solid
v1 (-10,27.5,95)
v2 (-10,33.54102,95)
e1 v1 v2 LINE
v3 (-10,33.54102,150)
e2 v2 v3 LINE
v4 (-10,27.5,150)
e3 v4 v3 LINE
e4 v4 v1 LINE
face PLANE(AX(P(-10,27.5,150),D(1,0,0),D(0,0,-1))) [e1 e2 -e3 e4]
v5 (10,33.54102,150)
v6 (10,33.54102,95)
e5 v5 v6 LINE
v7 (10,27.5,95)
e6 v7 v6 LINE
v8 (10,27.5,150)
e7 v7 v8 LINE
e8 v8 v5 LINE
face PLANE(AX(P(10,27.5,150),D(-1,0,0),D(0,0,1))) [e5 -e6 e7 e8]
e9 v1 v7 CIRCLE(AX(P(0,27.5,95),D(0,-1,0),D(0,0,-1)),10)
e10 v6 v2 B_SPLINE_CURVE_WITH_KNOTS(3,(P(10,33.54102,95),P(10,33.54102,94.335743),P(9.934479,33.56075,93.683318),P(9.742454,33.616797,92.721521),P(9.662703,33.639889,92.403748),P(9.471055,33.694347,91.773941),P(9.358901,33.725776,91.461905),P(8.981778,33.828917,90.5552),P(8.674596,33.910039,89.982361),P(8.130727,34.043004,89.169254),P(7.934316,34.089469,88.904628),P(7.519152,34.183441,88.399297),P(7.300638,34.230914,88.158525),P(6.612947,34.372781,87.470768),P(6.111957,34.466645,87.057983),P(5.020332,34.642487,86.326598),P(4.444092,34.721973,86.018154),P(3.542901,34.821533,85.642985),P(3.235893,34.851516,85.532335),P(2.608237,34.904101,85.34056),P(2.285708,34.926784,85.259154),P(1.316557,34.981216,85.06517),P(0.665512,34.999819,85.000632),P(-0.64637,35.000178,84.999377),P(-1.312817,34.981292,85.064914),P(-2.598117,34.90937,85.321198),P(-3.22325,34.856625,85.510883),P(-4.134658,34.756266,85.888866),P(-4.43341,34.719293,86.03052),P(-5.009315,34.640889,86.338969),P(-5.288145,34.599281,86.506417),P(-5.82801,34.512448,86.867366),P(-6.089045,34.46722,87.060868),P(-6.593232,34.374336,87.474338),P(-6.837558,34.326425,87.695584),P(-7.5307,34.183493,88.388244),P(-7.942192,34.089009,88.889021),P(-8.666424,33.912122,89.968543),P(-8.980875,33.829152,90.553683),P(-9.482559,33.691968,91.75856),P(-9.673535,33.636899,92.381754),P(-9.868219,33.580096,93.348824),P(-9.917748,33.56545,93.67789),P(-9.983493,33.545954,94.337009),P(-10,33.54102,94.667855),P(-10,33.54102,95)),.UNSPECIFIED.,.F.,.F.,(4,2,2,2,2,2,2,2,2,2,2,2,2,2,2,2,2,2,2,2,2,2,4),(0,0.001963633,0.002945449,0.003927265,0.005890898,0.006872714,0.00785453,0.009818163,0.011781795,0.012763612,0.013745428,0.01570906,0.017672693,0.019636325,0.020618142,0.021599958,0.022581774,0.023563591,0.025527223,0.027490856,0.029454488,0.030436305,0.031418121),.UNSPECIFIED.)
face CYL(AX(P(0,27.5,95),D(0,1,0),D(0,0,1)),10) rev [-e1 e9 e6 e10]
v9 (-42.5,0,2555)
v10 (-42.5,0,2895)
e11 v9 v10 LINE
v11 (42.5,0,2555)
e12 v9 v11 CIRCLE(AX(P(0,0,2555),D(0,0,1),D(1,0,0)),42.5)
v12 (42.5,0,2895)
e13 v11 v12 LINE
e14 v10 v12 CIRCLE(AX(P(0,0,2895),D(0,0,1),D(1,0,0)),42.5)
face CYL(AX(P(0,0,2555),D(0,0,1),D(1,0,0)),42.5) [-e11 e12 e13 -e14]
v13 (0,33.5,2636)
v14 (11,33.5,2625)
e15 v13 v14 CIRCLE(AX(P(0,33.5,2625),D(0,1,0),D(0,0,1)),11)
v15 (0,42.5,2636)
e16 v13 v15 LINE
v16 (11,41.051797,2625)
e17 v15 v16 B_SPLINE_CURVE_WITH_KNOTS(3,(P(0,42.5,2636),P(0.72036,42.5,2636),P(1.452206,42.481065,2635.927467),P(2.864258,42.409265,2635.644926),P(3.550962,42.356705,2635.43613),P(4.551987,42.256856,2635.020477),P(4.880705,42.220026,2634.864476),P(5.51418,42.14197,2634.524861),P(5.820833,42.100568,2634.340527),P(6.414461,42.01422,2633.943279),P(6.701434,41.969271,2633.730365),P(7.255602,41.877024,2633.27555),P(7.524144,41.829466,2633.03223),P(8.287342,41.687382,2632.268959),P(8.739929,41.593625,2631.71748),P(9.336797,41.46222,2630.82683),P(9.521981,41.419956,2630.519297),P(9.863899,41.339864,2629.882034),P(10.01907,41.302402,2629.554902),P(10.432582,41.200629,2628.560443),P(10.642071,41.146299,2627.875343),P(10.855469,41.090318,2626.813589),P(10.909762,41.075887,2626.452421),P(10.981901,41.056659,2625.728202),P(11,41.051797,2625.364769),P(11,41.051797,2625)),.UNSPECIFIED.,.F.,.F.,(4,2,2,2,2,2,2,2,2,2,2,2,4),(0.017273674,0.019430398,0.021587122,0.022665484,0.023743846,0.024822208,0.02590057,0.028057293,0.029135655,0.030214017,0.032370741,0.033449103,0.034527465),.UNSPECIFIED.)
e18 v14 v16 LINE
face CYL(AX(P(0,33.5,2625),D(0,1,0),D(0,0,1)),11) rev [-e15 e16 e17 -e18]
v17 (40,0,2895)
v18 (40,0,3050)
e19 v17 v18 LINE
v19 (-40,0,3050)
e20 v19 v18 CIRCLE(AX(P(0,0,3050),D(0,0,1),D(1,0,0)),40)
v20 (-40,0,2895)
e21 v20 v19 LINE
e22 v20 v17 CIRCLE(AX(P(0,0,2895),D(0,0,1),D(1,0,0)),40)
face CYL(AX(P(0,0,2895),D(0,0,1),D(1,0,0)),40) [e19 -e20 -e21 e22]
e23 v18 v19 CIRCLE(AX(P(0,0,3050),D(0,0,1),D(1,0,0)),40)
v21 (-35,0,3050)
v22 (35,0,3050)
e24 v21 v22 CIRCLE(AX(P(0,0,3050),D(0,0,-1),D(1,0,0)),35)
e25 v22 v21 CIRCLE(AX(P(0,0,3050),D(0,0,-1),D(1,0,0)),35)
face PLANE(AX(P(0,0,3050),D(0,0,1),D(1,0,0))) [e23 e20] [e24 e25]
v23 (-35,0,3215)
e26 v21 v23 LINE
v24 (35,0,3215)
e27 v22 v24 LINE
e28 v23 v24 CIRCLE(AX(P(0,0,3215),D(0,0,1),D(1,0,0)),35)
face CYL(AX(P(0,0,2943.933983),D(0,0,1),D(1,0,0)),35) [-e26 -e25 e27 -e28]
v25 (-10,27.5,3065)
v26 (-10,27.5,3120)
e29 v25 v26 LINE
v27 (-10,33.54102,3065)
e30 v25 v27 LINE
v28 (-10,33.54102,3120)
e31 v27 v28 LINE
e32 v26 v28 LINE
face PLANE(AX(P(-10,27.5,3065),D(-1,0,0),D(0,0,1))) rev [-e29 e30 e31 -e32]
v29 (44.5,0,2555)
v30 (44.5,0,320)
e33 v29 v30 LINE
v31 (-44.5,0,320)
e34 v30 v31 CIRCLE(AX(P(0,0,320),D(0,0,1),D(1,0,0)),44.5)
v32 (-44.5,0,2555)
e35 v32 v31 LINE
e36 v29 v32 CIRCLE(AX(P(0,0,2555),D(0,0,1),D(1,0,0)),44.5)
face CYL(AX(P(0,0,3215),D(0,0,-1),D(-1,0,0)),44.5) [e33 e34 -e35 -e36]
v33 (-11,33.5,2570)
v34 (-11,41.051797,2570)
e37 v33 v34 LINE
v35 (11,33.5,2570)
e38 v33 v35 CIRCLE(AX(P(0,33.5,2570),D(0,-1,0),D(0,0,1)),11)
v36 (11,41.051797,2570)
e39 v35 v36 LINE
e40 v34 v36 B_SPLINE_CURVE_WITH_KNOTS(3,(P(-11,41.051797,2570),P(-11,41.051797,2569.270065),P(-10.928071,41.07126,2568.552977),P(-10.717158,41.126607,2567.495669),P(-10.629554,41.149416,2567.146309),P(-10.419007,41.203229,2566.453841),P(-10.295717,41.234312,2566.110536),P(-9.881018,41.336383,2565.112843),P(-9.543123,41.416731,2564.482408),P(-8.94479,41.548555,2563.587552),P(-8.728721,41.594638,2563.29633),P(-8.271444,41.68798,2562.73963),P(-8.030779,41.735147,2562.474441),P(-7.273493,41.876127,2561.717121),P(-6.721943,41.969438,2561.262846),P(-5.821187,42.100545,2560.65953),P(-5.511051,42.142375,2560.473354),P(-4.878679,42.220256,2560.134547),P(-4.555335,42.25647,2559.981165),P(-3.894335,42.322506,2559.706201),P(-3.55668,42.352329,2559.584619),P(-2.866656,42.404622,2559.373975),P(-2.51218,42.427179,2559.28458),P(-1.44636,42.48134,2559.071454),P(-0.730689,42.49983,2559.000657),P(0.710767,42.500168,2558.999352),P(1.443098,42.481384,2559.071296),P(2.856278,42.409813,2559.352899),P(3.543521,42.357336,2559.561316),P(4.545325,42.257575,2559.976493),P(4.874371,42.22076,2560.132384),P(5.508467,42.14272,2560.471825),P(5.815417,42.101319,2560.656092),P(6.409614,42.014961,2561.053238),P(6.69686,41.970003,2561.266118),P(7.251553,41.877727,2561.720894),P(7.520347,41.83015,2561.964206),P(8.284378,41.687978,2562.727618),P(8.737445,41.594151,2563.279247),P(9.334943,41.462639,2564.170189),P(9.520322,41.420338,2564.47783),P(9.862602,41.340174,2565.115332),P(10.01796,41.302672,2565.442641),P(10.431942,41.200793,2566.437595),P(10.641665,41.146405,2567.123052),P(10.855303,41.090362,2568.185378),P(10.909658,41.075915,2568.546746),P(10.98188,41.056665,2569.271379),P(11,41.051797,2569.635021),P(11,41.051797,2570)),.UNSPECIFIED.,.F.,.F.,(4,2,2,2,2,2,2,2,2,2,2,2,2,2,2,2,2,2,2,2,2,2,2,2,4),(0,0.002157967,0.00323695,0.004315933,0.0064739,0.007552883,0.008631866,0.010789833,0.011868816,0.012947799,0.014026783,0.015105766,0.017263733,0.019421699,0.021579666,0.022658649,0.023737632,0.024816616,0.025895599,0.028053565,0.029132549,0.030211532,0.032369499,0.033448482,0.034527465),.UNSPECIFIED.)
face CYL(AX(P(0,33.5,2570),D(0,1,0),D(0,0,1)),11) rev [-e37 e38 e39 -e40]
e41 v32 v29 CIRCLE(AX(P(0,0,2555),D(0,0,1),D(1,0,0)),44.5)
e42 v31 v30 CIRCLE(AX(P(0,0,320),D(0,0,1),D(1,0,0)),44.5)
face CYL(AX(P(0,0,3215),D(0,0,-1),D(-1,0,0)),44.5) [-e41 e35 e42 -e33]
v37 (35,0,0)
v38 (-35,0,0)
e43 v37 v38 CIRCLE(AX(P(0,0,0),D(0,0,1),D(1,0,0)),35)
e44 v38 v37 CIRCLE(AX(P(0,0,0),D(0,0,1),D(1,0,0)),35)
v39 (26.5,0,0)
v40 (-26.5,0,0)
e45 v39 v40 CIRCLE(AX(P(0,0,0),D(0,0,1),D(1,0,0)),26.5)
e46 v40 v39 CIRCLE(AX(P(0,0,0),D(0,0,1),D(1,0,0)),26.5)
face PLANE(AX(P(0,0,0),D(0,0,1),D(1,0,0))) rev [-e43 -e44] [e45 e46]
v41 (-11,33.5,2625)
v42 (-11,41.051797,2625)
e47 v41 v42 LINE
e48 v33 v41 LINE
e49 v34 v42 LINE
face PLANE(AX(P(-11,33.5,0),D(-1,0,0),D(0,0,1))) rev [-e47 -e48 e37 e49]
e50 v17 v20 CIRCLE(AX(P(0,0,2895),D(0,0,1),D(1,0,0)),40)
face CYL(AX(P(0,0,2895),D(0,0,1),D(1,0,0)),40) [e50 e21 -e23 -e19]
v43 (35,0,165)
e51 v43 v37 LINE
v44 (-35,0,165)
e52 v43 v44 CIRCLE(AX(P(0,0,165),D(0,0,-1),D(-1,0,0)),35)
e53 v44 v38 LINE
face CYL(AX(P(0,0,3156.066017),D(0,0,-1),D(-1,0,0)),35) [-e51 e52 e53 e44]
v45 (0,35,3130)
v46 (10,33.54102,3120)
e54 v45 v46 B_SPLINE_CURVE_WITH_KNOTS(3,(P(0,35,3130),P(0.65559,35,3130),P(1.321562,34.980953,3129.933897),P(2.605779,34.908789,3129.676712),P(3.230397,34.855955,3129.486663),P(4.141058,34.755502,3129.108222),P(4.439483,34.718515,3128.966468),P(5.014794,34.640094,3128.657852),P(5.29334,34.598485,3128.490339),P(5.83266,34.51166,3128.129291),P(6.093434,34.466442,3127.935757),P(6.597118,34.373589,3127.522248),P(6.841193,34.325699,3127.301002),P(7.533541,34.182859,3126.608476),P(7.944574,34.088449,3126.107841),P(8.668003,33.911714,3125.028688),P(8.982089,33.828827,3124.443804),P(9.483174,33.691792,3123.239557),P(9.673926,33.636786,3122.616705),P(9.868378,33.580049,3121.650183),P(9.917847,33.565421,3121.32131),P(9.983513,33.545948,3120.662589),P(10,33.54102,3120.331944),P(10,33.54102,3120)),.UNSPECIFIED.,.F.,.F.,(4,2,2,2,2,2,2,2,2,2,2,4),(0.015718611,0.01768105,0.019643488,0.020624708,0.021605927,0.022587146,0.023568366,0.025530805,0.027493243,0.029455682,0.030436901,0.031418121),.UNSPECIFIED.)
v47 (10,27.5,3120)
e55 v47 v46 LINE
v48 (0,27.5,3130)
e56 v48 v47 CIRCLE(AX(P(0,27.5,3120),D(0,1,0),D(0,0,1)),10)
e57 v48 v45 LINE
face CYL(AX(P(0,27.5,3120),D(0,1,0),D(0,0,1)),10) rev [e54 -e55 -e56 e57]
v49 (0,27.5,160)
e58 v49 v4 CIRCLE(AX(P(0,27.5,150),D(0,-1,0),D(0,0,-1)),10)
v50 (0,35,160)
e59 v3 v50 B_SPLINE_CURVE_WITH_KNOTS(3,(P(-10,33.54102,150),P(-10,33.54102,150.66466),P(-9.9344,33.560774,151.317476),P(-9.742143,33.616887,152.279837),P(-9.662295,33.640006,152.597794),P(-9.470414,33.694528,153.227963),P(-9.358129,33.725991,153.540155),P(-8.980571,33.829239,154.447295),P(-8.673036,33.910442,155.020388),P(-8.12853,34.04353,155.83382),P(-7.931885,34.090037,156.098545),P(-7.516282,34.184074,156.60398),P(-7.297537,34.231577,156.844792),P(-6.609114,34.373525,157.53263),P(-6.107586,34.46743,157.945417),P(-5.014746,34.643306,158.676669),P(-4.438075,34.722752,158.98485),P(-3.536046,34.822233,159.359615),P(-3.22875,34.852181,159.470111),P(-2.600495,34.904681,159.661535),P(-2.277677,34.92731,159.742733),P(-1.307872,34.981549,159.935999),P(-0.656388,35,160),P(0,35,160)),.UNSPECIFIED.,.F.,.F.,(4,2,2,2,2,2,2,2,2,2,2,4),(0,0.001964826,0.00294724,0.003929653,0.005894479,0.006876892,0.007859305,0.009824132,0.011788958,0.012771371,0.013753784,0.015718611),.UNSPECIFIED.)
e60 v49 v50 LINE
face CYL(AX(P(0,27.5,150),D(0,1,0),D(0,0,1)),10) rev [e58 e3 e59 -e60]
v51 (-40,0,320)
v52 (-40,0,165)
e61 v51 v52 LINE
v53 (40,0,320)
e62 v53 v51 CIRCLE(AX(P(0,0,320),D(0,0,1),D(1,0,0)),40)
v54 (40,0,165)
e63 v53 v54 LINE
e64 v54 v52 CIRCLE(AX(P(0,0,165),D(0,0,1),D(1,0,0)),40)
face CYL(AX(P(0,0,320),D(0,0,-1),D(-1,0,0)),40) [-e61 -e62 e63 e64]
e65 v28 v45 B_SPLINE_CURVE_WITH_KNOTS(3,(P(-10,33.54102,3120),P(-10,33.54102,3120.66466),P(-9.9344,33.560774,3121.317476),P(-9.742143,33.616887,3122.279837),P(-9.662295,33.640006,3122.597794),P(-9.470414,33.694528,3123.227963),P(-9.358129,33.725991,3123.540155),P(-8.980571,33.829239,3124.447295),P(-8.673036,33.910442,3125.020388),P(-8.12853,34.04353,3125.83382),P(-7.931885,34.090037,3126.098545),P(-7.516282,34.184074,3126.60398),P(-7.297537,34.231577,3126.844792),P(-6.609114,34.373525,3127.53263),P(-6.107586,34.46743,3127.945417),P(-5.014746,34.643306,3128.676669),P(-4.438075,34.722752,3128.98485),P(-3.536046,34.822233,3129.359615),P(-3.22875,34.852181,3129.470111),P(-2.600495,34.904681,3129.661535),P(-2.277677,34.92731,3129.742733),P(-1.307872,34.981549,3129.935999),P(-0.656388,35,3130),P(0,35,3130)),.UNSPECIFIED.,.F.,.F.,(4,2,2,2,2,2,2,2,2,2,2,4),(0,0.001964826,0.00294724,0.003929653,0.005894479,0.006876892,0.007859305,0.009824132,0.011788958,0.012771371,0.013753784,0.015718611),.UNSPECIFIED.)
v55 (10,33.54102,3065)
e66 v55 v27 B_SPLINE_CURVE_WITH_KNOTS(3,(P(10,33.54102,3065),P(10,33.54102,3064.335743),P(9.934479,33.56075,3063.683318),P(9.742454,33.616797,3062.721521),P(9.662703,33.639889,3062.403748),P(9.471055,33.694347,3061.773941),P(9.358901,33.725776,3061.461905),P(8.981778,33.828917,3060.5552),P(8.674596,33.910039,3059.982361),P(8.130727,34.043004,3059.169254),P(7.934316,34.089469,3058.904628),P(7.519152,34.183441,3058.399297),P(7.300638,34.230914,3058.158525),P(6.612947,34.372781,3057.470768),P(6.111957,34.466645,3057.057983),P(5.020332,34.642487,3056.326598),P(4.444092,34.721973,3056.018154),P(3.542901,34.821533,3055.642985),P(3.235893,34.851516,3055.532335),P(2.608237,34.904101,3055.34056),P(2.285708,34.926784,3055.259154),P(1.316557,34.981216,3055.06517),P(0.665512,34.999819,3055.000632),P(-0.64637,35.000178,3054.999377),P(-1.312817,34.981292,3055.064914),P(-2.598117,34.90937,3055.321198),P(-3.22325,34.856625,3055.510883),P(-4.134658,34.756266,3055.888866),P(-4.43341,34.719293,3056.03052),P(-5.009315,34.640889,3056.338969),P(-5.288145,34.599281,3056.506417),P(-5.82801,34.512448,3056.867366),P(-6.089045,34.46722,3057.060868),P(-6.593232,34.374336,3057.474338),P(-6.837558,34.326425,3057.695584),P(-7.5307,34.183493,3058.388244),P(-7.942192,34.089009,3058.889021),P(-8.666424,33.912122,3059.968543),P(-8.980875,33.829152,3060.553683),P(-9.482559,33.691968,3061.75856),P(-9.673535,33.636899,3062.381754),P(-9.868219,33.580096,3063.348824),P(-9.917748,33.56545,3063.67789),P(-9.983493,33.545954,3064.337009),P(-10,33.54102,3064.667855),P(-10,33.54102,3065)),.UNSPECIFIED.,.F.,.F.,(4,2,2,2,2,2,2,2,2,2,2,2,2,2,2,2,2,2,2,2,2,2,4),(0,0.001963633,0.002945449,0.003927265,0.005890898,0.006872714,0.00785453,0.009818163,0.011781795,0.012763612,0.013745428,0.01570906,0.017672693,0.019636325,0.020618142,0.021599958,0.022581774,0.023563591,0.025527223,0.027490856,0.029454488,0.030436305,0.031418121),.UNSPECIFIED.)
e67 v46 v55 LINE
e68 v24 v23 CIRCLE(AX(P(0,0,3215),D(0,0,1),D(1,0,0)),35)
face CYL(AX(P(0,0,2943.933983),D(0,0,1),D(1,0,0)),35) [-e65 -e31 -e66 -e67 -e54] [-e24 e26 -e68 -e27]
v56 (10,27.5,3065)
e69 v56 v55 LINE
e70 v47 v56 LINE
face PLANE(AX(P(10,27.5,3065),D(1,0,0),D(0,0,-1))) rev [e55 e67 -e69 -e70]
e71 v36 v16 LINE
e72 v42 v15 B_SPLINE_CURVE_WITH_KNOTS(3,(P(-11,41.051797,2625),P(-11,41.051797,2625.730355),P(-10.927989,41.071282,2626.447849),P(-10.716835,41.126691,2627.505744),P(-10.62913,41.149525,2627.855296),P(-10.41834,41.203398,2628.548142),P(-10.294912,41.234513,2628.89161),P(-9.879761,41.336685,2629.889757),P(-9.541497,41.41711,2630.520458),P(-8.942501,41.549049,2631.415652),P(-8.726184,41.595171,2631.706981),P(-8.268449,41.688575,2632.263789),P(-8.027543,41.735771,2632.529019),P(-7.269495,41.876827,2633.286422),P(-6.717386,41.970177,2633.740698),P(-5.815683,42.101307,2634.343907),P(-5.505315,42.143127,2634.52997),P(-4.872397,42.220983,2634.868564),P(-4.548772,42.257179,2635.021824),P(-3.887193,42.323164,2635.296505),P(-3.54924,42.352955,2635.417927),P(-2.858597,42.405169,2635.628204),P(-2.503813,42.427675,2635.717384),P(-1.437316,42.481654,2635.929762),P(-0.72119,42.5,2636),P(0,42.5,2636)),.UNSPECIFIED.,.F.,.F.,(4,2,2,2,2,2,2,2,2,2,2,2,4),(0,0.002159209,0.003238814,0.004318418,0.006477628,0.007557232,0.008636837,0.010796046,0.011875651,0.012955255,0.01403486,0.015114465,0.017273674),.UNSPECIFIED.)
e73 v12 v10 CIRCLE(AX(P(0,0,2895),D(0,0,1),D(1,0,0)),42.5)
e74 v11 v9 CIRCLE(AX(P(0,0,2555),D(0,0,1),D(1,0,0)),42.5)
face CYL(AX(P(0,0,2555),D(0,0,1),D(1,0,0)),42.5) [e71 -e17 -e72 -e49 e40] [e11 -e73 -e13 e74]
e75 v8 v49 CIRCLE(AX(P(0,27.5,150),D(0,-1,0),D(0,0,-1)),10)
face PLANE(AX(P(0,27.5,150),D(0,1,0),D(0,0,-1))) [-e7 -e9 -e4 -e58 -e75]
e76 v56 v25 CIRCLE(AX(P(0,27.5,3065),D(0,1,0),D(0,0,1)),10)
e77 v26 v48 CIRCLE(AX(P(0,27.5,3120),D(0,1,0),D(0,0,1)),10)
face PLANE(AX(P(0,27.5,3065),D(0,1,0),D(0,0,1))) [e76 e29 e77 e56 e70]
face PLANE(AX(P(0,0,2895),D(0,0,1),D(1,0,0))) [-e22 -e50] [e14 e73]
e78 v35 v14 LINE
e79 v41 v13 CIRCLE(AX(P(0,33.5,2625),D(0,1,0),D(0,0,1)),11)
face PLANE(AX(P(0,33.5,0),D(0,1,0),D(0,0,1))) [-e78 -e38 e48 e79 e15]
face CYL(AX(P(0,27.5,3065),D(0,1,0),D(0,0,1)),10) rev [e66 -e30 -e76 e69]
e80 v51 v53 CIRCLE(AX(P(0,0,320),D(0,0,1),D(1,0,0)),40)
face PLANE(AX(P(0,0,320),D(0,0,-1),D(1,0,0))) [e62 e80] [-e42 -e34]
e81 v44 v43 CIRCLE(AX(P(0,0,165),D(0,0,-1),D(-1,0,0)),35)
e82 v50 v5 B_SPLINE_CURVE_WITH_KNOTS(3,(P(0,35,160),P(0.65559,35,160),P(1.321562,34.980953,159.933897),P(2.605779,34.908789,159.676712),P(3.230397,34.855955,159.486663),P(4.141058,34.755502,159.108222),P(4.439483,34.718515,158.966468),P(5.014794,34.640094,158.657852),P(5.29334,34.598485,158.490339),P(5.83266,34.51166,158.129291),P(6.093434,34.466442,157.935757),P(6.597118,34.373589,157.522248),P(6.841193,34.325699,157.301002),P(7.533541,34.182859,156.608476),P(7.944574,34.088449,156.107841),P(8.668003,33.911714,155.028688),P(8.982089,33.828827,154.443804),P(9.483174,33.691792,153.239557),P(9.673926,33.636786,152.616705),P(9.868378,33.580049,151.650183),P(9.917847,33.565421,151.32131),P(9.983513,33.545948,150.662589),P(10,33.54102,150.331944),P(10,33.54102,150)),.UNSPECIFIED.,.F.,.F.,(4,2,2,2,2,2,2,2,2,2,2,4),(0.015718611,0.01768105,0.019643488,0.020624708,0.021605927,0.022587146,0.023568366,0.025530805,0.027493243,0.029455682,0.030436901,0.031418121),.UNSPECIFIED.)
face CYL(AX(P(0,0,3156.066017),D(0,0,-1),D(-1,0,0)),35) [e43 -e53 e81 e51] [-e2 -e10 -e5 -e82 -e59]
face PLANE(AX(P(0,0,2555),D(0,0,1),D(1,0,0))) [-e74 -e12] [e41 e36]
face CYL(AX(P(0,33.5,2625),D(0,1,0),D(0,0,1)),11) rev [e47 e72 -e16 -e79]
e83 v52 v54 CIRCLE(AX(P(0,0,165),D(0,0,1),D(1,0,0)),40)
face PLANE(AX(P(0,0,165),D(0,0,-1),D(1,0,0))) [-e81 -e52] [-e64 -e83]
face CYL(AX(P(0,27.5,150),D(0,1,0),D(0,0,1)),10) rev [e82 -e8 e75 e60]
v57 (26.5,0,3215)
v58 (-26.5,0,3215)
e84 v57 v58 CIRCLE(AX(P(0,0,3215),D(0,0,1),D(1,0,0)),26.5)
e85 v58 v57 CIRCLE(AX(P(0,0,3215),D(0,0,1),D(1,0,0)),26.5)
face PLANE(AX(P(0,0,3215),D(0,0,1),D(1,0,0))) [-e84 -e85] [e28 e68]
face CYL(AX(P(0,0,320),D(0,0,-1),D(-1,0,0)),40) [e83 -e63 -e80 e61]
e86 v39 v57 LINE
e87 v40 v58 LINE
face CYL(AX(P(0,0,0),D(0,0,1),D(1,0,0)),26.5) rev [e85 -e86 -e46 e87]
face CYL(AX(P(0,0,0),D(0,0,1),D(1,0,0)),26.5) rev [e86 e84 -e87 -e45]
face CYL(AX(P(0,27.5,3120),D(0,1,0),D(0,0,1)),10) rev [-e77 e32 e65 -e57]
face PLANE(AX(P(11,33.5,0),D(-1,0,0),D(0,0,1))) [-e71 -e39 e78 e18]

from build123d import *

# Parameters (mm, degrees)
SKETCH1_R           = 44.5
BOSS_EXTRUDE1_DEPTH = 3215
CUT_EXTRUDE1_START  = -165
SKETCH2_R           = 44.5
SKETCH2_R_2         = 37.5
CUT_EXTRUDE1_DEPTH  = 165
CUT_EXTRUDE2_START  = -155
SKETCH3_R           = 44.5
SKETCH3_R_2         = 40
CUT_EXTRUDE2_DEPTH  = 155
CUT_EXTRUDE3_START  = -340
SKETCH4_R           = 44.5
SKETCH4_R_2         = 42.5
CUT_EXTRUDE3_DEPTH  = 340
SKETCH8_R           = 26.5
CUT_EXTRUDE7_DEPTH  = 3216.615881911
CUT_EXTRUDE8_START  = -165
SKETCH10_R          = 37.5
SKETCH10_R_2        = 35
CUT_EXTRUDE8_DEPTH  = 165
CUT_EXTRUDE9_DEPTH  = 7.5
CUT_EXTRUDE10_DEPTH = 9


with BuildPart() as part:
    # Sketch1 → Boss-Extrude1 (new body)
    with BuildSketch(Plane.XY):
        with Locations(Location((0, 0, 0), (0, 0, 180))):
            Circle(SKETCH1_R)
    extrude(amount=BOSS_EXTRUDE1_DEPTH)

    # Sketch2 → Cut-Extrude1 (cut)
    with BuildSketch(Plane.XY.offset(3215).offset(CUT_EXTRUDE1_START)):
        with Locations(Location((0, 0, 0), (0, 0, 180))):
            Circle(SKETCH2_R)
        Circle(SKETCH2_R_2, mode=Mode.SUBTRACT)
    cut_extrude1 = extrude(amount=CUT_EXTRUDE1_DEPTH, mode=Mode.SUBTRACT)

    # Sketch3 → Cut-Extrude2 (cut)
    with BuildSketch(Plane.XY.offset(3050).offset(CUT_EXTRUDE2_START)):
        with Locations(Location((0, 0, 0), (0, 0, 180))):
            Circle(SKETCH3_R)
        Circle(SKETCH3_R_2, mode=Mode.SUBTRACT)
    cut_extrude2 = extrude(amount=CUT_EXTRUDE2_DEPTH, mode=Mode.SUBTRACT)

    # Sketch4 → Cut-Extrude3 (cut)
    with BuildSketch(Plane.XY.offset(2895).offset(CUT_EXTRUDE3_START)):
        with Locations(Location((0, 0, 0), (0, 0, 180))):
            Circle(SKETCH4_R)
        Circle(SKETCH4_R_2, mode=Mode.SUBTRACT)
    extrude(amount=CUT_EXTRUDE3_DEPTH, mode=Mode.SUBTRACT)

    # Sketch8 → Cut-Extrude7 (cut, through all)
    with BuildSketch(Plane.XY.offset(3215)):
        Circle(SKETCH8_R)
    extrude(amount=-CUT_EXTRUDE7_DEPTH, mode=Mode.SUBTRACT)

    # Sketch10 → Cut-Extrude8 (cut)
    with BuildSketch(Plane.XY.offset(3215).offset(CUT_EXTRUDE8_START)):
        Circle(SKETCH10_R)
        Circle(SKETCH10_R_2, mode=Mode.SUBTRACT)
    cut_extrude8 = extrude(amount=CUT_EXTRUDE8_DEPTH, mode=Mode.SUBTRACT)

    # Mirror1: Cut-Extrude1, Cut-Extrude2, Cut-Extrude8 across plane
    add(cut_extrude1.mirror(Plane.XY.offset(1607.5)), mode=Mode.SUBTRACT)
    add(cut_extrude2.mirror(Plane.XY.offset(1607.5)), mode=Mode.SUBTRACT)
    add(cut_extrude8.mirror(Plane.XY.offset(1607.5)), mode=Mode.SUBTRACT)

    # Sketch11 → Cut-Extrude9 (cut)
    with BuildSketch(Plane(origin=(0, 35, 0), x_dir=(1, 0, 0), z_dir=(0, 1, 0))):
        with BuildLine():
            Line((10, -3065), (10, -3120))
            ThreePointArc((10, -3120), (0, -3130), (-10, -3120))
            Line((-10, -3120), (-10, -3065))
            ThreePointArc((-10, -3065), (0, -3055), (10, -3065))
        make_face()
    cut_extrude9 = extrude(amount=-CUT_EXTRUDE9_DEPTH, mode=Mode.SUBTRACT)

    # Mirror2: Cut-Extrude9 across plane
    add(cut_extrude9.mirror(Plane.XY.offset(1607.5)), mode=Mode.SUBTRACT)

    # Sketch12 → Cut-Extrude10 (cut)
    with BuildSketch(Plane(origin=(0, 42.5, 0), x_dir=(1, 0, 0), z_dir=(0, 1, 0))):
        with BuildLine():
            Line((11, -2570), (11, -2625))
            ThreePointArc((11, -2625), (0, -2636), (-11, -2625))
            Line((-11, -2625), (-11, -2570))
            ThreePointArc((-11, -2570), (0, -2559), (11, -2570))
        make_face()
    extrude(amount=-CUT_EXTRUDE10_DEPTH, mode=Mode.SUBTRACT)


solid = part.part
